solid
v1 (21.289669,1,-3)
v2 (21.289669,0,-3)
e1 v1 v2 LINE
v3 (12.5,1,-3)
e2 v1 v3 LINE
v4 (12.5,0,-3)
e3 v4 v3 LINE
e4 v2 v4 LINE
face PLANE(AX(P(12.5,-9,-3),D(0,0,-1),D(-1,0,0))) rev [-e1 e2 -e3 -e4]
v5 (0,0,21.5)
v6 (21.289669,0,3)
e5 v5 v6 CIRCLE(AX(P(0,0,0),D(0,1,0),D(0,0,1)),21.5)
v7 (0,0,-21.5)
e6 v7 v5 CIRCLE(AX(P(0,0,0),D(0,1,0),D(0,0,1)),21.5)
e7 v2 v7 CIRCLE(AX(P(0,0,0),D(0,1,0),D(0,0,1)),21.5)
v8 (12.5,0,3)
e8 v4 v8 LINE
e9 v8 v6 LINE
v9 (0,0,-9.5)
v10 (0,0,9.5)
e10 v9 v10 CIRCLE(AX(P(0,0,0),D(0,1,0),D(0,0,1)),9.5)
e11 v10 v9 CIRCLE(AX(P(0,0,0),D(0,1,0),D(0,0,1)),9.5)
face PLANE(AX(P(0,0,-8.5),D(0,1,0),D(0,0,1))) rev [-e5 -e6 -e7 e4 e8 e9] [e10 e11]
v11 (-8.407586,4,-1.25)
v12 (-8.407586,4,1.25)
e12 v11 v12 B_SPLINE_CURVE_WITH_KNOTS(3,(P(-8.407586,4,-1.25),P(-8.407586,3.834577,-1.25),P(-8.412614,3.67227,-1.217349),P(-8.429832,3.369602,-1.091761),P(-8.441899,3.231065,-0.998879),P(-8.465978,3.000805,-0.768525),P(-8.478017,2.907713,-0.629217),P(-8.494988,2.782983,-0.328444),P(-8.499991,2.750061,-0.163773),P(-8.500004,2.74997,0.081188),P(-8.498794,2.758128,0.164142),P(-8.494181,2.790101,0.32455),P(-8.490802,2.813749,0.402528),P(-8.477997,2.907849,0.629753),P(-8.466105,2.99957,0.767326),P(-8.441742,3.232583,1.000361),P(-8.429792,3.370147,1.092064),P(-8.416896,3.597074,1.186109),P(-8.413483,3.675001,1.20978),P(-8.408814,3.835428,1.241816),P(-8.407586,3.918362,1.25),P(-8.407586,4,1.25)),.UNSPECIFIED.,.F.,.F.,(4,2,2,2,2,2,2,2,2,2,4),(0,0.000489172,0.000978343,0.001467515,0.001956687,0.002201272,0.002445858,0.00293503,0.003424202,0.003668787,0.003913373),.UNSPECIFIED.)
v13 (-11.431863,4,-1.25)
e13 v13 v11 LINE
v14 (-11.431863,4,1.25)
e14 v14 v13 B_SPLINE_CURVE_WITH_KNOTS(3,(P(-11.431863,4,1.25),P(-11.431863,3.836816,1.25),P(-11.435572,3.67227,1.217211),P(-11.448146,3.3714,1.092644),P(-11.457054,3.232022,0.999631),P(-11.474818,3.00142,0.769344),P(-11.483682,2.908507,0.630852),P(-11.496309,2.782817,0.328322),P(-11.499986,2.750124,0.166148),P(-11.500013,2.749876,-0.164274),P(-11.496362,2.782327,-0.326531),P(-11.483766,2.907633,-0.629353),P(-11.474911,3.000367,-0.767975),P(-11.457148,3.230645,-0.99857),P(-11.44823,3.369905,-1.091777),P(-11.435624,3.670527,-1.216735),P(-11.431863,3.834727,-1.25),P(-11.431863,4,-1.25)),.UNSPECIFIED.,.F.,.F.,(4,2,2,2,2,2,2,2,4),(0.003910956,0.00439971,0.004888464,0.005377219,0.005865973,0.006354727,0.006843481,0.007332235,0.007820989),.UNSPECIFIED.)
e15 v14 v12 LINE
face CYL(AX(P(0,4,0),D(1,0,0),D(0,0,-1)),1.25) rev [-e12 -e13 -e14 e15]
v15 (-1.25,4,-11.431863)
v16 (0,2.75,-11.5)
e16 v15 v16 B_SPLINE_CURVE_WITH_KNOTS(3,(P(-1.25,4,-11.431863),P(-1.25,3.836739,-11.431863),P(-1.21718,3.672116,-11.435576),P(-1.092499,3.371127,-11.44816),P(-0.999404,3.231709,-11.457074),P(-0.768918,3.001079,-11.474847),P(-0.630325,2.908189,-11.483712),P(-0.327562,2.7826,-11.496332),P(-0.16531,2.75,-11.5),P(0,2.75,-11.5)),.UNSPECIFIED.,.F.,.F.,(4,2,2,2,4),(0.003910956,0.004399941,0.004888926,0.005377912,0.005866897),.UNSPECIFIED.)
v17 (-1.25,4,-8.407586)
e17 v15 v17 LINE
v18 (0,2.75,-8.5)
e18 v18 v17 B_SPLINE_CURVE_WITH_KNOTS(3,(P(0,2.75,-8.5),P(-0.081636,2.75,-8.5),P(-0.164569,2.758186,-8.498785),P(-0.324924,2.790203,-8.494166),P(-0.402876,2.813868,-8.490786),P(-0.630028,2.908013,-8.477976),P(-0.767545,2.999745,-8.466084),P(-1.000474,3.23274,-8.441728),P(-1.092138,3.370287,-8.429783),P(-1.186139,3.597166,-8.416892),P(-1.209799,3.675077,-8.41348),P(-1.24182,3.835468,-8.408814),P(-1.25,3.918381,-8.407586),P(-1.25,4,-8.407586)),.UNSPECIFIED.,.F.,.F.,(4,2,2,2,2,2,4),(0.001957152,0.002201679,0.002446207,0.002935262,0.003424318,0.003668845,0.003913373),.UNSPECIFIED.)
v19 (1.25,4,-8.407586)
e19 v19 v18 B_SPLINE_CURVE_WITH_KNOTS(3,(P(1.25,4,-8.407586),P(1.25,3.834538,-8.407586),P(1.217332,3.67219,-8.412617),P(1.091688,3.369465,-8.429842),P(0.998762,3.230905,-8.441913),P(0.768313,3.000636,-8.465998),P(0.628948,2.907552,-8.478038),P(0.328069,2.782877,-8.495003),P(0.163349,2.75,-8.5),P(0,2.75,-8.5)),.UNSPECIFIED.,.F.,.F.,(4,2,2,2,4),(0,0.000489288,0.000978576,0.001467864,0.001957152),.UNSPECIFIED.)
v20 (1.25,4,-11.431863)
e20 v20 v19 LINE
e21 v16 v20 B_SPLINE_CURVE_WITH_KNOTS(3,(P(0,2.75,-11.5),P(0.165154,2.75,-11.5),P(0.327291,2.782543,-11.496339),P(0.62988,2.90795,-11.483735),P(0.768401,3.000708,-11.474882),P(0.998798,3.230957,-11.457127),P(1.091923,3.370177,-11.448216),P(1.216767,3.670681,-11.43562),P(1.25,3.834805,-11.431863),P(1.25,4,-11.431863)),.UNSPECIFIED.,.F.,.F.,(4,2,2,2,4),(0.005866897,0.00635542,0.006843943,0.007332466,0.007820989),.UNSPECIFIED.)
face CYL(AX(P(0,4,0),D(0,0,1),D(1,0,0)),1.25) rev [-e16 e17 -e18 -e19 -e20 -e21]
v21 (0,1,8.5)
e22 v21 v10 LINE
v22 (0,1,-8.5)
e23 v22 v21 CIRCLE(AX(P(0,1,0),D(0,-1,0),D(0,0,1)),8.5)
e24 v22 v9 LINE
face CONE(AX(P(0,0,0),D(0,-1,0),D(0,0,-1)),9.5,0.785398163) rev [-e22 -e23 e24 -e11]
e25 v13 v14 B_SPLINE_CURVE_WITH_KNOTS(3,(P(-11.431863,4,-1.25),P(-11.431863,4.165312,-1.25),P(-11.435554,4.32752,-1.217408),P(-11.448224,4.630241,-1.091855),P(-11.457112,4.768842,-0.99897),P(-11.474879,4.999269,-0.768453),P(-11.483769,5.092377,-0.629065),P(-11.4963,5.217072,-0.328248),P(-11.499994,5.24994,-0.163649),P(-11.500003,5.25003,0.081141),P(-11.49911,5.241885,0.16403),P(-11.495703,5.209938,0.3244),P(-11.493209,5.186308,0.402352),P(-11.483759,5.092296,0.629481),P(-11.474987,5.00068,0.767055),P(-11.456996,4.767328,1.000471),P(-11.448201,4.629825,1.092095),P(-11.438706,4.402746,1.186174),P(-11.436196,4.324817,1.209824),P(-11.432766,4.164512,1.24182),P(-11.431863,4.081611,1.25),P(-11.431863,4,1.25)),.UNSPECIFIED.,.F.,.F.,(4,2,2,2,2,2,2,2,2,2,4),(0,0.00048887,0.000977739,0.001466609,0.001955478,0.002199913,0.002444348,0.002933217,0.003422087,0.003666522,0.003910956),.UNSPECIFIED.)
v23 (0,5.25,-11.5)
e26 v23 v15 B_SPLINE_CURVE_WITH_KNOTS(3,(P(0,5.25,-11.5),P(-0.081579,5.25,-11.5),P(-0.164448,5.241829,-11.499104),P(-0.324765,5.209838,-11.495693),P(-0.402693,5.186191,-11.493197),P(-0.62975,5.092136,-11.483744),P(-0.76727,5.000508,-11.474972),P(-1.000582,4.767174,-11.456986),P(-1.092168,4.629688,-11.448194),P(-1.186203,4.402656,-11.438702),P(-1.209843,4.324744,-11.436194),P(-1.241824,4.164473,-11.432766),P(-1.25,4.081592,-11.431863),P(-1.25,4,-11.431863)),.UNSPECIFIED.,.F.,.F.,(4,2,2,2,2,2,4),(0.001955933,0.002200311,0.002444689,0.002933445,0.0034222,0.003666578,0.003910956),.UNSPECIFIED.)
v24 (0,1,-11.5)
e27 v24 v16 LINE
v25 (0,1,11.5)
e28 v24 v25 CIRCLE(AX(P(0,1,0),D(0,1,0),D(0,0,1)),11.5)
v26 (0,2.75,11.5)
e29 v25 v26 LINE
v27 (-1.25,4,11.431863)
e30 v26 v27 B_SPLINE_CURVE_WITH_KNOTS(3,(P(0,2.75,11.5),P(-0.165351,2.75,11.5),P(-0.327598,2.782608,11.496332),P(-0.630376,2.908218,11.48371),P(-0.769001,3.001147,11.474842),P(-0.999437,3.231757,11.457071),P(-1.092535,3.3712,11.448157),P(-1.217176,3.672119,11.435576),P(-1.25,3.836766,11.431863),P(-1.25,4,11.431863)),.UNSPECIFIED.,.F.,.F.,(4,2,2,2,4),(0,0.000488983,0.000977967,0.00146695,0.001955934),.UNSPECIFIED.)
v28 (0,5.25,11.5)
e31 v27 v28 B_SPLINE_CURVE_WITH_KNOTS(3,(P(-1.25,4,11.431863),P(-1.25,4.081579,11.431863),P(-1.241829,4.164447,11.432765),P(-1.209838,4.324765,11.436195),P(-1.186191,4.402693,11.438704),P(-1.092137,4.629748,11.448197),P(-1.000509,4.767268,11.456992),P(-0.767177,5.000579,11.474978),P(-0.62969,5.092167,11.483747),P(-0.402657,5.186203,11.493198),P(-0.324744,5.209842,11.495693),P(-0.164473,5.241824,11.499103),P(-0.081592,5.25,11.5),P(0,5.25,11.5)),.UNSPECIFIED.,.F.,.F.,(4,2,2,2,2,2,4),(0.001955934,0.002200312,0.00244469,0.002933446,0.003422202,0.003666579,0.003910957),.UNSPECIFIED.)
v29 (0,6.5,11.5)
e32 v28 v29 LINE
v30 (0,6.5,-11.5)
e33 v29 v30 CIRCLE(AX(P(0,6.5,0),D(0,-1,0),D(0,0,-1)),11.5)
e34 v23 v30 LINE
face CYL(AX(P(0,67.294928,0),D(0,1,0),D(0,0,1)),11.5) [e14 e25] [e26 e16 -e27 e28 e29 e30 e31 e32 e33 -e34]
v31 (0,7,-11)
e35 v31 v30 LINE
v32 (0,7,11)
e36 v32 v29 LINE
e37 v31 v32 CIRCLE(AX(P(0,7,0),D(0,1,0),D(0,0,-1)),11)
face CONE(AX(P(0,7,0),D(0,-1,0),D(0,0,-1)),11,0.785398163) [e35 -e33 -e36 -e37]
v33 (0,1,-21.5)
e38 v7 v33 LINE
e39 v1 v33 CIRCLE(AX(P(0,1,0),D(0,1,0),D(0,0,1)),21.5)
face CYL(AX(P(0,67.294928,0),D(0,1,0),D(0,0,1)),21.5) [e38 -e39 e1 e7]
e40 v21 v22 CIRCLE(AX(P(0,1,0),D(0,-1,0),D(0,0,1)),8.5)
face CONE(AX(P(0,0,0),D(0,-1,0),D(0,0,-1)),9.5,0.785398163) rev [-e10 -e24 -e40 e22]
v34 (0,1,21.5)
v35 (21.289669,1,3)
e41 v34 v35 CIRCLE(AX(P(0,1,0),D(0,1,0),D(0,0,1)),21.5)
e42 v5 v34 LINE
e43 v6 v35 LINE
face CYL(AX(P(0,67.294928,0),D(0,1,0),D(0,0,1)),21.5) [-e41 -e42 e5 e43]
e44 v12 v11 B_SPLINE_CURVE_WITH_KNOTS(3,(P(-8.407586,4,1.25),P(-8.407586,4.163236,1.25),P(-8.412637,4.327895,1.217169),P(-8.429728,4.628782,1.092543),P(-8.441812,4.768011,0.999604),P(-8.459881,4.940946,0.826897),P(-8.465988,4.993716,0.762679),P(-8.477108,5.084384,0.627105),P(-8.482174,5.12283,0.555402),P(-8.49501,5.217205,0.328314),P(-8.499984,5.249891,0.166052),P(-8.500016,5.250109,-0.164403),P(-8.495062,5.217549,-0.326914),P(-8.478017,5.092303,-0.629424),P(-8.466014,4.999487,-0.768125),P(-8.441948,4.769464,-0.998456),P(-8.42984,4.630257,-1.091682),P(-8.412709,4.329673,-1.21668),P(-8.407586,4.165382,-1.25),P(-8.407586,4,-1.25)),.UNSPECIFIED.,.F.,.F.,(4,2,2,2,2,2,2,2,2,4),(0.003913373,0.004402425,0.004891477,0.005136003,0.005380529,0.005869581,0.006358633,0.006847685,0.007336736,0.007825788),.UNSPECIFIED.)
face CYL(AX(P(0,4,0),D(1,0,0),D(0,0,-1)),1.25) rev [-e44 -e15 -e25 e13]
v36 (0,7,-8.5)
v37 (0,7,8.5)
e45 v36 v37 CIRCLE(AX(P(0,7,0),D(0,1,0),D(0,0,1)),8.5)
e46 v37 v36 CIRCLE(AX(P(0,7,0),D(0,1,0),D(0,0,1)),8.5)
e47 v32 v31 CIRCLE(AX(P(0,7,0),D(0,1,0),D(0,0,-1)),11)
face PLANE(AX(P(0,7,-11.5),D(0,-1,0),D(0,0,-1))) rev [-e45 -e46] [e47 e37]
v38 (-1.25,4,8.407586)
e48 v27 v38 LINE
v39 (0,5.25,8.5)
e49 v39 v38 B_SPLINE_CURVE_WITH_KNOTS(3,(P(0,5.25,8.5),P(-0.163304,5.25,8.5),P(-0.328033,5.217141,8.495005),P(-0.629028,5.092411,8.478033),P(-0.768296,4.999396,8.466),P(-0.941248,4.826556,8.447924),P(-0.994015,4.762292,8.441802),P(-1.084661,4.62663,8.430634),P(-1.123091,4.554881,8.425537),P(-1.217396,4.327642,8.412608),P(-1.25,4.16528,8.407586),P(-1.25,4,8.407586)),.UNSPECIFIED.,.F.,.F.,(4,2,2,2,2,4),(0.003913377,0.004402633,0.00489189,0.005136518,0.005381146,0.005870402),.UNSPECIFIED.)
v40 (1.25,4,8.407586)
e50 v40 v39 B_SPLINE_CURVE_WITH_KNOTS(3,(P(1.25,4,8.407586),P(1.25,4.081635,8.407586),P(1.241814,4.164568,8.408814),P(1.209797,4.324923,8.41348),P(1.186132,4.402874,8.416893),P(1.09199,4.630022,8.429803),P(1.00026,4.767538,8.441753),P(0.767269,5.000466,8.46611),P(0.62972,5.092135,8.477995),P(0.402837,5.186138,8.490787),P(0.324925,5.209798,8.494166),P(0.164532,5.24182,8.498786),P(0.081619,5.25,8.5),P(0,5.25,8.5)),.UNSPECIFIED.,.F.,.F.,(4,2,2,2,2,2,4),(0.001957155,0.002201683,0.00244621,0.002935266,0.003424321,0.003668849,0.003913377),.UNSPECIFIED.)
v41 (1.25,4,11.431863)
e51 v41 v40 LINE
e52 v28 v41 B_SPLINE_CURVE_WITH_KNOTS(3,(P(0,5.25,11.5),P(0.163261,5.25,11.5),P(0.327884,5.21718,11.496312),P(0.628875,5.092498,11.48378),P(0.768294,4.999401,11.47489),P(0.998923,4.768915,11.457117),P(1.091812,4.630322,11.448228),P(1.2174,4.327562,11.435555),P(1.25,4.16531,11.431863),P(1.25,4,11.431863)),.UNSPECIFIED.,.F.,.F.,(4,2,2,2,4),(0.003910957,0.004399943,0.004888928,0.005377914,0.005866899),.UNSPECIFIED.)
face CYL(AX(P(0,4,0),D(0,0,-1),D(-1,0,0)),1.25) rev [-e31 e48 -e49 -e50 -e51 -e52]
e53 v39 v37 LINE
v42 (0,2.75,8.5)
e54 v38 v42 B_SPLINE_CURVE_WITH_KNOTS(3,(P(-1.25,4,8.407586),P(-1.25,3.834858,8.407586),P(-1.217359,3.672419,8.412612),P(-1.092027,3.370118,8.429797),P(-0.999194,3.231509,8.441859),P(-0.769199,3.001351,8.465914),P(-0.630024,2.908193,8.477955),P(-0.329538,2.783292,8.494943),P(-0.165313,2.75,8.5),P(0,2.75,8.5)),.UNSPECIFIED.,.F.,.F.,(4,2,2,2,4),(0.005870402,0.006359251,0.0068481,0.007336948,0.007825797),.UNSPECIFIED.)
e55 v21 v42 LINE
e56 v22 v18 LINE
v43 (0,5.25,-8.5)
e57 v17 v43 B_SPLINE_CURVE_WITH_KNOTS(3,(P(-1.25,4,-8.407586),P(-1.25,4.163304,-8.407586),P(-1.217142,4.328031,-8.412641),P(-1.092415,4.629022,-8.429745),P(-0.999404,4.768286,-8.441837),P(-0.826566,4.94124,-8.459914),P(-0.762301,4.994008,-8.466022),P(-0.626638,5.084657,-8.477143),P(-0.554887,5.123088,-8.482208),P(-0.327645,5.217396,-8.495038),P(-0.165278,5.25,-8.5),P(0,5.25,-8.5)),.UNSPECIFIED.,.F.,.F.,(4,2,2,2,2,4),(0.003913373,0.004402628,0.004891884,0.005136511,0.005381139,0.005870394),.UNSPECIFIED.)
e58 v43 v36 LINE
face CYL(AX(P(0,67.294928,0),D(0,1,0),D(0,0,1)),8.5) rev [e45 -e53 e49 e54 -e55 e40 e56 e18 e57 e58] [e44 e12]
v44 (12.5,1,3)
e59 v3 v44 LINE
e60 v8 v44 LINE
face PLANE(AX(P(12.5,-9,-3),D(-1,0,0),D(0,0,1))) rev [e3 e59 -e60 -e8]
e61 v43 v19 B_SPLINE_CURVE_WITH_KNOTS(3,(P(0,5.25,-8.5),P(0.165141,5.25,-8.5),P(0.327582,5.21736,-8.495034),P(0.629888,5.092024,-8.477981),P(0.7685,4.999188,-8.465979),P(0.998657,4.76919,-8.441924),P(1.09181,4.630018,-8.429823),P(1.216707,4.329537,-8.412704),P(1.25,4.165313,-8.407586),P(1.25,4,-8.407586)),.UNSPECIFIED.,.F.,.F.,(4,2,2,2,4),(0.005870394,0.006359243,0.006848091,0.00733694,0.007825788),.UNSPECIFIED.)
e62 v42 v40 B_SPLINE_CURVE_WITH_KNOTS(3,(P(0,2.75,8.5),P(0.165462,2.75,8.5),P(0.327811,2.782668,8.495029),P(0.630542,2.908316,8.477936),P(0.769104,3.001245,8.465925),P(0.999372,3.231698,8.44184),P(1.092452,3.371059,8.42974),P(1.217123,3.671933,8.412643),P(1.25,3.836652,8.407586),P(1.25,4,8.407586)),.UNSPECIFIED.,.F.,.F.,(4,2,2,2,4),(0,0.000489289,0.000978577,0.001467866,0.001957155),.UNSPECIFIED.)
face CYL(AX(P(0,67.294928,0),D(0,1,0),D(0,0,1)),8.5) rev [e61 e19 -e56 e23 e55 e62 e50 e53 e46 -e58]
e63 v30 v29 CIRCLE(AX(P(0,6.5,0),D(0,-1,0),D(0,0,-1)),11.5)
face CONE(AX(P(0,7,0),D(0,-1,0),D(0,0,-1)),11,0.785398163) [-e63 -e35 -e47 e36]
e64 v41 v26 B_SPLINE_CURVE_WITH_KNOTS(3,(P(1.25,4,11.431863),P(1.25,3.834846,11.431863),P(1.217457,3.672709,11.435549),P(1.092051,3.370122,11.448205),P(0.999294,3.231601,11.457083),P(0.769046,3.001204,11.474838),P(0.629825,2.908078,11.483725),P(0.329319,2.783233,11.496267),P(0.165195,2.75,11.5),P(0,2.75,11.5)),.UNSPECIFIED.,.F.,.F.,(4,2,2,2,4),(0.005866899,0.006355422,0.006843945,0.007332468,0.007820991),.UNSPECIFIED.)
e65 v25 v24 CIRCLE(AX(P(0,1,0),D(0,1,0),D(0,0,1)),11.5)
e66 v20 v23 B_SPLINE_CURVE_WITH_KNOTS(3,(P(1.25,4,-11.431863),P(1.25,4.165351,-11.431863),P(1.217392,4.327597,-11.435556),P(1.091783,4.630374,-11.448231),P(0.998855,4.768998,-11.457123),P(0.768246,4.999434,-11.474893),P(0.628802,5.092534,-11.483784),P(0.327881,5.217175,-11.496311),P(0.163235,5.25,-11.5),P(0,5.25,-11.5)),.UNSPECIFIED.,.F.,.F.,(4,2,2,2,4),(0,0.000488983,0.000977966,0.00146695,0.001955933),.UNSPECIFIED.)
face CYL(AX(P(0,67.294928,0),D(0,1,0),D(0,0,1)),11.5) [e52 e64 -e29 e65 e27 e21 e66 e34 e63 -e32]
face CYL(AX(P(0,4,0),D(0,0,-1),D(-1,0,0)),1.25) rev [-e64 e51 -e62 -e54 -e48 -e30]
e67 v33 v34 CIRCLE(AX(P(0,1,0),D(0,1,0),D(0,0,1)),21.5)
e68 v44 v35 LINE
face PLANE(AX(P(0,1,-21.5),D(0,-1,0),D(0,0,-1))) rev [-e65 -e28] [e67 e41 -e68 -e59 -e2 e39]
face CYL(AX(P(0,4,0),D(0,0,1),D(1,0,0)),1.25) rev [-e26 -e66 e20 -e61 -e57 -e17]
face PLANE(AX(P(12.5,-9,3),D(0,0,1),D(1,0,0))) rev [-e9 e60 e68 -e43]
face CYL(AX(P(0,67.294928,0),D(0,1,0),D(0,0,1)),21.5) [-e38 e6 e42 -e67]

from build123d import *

# Parameters (mm, degrees)
CHAMFER1_SIZE      = 1
SKETCH7_W          = 11.256792451
SKETCH7_H          = 6
CUT_EXTRUDE1_DEPTH = 10
SKETCH9_W          = 1.25
SKETCH9_H          = 21.5
CHAMFER2_SIZE      = 0.5
CIRPATTERN1_COUNT  = 4


with BuildPart() as part:
    # Sketch2 → Revolve1 (revolve)
    with BuildSketch(Plane(origin=(0, 0, 0), x_dir=(0, 0, -1), z_dir=(1, 0, 0)), mode=Mode.PRIVATE) as revolve1_sk:
        Polygon((8.5, 0), (21.5, 0), (21.5, 1), (11.5, 1), (11.5, 7), (8.5, 7), align=None)
    revolve(revolve1_sk.sketch.rotate(Axis((0, 67.294927727, 0), (0, -1, 0)), 180), axis=Axis((0, 67.294927727, 0), (0, -1, 0)))

    # Chamfer1
    chamfer1_edges = [part.edges().sort_by_distance(p)[0] for p in [
        (0, 0, -8.5),
    ]]
    chamfer(chamfer1_edges, length=CHAMFER1_SIZE)

    # Sketch7 → Cut-Extrude1 (cut)
    with BuildSketch(Plane(origin=(0, 1, 0), x_dir=(1, 0, 0), z_dir=(0, 1, 0))):
        with Locations((18.128396226, 0)):
            Rectangle(SKETCH7_W, SKETCH7_H)
    extrude(amount=-CUT_EXTRUDE1_DEPTH, mode=Mode.SUBTRACT)

    # Sketch9 → M3 Tapped Hole2 (revolve, cut)
    with BuildSketch(Plane(origin=(0, 4, 0), x_dir=(0, 0, -1), z_dir=(0, 1, 0))):
        with Locations((0.625, 10.75)):
            Rectangle(SKETCH9_W, SKETCH9_H)
    m3_tapped_hole2 = revolve(axis=Axis((6.35, 4, 0), (-1, 0, 0)), mode=Mode.SUBTRACT)

    # Chamfer2
    chamfer2_edges = [part.edges().sort_by_distance(p)[0] for p in [
        (0, 7, -11.5),
    ]]
    chamfer(chamfer2_edges, length=CHAMFER2_SIZE)

    # CirPattern1: M3 Tapped Hole2 ×4 about axis, 1 skipped
    cirpattern1_axis = Axis((0, 67.294927727, 0), (0, 1, 0))
    add([m3_tapped_hole2.rotate(cirpattern1_axis, i * 360 / CIRPATTERN1_COUNT) for i in range(1, CIRPATTERN1_COUNT) if i not in (2,)], mode=Mode.SUBTRACT)


solid = part.part
